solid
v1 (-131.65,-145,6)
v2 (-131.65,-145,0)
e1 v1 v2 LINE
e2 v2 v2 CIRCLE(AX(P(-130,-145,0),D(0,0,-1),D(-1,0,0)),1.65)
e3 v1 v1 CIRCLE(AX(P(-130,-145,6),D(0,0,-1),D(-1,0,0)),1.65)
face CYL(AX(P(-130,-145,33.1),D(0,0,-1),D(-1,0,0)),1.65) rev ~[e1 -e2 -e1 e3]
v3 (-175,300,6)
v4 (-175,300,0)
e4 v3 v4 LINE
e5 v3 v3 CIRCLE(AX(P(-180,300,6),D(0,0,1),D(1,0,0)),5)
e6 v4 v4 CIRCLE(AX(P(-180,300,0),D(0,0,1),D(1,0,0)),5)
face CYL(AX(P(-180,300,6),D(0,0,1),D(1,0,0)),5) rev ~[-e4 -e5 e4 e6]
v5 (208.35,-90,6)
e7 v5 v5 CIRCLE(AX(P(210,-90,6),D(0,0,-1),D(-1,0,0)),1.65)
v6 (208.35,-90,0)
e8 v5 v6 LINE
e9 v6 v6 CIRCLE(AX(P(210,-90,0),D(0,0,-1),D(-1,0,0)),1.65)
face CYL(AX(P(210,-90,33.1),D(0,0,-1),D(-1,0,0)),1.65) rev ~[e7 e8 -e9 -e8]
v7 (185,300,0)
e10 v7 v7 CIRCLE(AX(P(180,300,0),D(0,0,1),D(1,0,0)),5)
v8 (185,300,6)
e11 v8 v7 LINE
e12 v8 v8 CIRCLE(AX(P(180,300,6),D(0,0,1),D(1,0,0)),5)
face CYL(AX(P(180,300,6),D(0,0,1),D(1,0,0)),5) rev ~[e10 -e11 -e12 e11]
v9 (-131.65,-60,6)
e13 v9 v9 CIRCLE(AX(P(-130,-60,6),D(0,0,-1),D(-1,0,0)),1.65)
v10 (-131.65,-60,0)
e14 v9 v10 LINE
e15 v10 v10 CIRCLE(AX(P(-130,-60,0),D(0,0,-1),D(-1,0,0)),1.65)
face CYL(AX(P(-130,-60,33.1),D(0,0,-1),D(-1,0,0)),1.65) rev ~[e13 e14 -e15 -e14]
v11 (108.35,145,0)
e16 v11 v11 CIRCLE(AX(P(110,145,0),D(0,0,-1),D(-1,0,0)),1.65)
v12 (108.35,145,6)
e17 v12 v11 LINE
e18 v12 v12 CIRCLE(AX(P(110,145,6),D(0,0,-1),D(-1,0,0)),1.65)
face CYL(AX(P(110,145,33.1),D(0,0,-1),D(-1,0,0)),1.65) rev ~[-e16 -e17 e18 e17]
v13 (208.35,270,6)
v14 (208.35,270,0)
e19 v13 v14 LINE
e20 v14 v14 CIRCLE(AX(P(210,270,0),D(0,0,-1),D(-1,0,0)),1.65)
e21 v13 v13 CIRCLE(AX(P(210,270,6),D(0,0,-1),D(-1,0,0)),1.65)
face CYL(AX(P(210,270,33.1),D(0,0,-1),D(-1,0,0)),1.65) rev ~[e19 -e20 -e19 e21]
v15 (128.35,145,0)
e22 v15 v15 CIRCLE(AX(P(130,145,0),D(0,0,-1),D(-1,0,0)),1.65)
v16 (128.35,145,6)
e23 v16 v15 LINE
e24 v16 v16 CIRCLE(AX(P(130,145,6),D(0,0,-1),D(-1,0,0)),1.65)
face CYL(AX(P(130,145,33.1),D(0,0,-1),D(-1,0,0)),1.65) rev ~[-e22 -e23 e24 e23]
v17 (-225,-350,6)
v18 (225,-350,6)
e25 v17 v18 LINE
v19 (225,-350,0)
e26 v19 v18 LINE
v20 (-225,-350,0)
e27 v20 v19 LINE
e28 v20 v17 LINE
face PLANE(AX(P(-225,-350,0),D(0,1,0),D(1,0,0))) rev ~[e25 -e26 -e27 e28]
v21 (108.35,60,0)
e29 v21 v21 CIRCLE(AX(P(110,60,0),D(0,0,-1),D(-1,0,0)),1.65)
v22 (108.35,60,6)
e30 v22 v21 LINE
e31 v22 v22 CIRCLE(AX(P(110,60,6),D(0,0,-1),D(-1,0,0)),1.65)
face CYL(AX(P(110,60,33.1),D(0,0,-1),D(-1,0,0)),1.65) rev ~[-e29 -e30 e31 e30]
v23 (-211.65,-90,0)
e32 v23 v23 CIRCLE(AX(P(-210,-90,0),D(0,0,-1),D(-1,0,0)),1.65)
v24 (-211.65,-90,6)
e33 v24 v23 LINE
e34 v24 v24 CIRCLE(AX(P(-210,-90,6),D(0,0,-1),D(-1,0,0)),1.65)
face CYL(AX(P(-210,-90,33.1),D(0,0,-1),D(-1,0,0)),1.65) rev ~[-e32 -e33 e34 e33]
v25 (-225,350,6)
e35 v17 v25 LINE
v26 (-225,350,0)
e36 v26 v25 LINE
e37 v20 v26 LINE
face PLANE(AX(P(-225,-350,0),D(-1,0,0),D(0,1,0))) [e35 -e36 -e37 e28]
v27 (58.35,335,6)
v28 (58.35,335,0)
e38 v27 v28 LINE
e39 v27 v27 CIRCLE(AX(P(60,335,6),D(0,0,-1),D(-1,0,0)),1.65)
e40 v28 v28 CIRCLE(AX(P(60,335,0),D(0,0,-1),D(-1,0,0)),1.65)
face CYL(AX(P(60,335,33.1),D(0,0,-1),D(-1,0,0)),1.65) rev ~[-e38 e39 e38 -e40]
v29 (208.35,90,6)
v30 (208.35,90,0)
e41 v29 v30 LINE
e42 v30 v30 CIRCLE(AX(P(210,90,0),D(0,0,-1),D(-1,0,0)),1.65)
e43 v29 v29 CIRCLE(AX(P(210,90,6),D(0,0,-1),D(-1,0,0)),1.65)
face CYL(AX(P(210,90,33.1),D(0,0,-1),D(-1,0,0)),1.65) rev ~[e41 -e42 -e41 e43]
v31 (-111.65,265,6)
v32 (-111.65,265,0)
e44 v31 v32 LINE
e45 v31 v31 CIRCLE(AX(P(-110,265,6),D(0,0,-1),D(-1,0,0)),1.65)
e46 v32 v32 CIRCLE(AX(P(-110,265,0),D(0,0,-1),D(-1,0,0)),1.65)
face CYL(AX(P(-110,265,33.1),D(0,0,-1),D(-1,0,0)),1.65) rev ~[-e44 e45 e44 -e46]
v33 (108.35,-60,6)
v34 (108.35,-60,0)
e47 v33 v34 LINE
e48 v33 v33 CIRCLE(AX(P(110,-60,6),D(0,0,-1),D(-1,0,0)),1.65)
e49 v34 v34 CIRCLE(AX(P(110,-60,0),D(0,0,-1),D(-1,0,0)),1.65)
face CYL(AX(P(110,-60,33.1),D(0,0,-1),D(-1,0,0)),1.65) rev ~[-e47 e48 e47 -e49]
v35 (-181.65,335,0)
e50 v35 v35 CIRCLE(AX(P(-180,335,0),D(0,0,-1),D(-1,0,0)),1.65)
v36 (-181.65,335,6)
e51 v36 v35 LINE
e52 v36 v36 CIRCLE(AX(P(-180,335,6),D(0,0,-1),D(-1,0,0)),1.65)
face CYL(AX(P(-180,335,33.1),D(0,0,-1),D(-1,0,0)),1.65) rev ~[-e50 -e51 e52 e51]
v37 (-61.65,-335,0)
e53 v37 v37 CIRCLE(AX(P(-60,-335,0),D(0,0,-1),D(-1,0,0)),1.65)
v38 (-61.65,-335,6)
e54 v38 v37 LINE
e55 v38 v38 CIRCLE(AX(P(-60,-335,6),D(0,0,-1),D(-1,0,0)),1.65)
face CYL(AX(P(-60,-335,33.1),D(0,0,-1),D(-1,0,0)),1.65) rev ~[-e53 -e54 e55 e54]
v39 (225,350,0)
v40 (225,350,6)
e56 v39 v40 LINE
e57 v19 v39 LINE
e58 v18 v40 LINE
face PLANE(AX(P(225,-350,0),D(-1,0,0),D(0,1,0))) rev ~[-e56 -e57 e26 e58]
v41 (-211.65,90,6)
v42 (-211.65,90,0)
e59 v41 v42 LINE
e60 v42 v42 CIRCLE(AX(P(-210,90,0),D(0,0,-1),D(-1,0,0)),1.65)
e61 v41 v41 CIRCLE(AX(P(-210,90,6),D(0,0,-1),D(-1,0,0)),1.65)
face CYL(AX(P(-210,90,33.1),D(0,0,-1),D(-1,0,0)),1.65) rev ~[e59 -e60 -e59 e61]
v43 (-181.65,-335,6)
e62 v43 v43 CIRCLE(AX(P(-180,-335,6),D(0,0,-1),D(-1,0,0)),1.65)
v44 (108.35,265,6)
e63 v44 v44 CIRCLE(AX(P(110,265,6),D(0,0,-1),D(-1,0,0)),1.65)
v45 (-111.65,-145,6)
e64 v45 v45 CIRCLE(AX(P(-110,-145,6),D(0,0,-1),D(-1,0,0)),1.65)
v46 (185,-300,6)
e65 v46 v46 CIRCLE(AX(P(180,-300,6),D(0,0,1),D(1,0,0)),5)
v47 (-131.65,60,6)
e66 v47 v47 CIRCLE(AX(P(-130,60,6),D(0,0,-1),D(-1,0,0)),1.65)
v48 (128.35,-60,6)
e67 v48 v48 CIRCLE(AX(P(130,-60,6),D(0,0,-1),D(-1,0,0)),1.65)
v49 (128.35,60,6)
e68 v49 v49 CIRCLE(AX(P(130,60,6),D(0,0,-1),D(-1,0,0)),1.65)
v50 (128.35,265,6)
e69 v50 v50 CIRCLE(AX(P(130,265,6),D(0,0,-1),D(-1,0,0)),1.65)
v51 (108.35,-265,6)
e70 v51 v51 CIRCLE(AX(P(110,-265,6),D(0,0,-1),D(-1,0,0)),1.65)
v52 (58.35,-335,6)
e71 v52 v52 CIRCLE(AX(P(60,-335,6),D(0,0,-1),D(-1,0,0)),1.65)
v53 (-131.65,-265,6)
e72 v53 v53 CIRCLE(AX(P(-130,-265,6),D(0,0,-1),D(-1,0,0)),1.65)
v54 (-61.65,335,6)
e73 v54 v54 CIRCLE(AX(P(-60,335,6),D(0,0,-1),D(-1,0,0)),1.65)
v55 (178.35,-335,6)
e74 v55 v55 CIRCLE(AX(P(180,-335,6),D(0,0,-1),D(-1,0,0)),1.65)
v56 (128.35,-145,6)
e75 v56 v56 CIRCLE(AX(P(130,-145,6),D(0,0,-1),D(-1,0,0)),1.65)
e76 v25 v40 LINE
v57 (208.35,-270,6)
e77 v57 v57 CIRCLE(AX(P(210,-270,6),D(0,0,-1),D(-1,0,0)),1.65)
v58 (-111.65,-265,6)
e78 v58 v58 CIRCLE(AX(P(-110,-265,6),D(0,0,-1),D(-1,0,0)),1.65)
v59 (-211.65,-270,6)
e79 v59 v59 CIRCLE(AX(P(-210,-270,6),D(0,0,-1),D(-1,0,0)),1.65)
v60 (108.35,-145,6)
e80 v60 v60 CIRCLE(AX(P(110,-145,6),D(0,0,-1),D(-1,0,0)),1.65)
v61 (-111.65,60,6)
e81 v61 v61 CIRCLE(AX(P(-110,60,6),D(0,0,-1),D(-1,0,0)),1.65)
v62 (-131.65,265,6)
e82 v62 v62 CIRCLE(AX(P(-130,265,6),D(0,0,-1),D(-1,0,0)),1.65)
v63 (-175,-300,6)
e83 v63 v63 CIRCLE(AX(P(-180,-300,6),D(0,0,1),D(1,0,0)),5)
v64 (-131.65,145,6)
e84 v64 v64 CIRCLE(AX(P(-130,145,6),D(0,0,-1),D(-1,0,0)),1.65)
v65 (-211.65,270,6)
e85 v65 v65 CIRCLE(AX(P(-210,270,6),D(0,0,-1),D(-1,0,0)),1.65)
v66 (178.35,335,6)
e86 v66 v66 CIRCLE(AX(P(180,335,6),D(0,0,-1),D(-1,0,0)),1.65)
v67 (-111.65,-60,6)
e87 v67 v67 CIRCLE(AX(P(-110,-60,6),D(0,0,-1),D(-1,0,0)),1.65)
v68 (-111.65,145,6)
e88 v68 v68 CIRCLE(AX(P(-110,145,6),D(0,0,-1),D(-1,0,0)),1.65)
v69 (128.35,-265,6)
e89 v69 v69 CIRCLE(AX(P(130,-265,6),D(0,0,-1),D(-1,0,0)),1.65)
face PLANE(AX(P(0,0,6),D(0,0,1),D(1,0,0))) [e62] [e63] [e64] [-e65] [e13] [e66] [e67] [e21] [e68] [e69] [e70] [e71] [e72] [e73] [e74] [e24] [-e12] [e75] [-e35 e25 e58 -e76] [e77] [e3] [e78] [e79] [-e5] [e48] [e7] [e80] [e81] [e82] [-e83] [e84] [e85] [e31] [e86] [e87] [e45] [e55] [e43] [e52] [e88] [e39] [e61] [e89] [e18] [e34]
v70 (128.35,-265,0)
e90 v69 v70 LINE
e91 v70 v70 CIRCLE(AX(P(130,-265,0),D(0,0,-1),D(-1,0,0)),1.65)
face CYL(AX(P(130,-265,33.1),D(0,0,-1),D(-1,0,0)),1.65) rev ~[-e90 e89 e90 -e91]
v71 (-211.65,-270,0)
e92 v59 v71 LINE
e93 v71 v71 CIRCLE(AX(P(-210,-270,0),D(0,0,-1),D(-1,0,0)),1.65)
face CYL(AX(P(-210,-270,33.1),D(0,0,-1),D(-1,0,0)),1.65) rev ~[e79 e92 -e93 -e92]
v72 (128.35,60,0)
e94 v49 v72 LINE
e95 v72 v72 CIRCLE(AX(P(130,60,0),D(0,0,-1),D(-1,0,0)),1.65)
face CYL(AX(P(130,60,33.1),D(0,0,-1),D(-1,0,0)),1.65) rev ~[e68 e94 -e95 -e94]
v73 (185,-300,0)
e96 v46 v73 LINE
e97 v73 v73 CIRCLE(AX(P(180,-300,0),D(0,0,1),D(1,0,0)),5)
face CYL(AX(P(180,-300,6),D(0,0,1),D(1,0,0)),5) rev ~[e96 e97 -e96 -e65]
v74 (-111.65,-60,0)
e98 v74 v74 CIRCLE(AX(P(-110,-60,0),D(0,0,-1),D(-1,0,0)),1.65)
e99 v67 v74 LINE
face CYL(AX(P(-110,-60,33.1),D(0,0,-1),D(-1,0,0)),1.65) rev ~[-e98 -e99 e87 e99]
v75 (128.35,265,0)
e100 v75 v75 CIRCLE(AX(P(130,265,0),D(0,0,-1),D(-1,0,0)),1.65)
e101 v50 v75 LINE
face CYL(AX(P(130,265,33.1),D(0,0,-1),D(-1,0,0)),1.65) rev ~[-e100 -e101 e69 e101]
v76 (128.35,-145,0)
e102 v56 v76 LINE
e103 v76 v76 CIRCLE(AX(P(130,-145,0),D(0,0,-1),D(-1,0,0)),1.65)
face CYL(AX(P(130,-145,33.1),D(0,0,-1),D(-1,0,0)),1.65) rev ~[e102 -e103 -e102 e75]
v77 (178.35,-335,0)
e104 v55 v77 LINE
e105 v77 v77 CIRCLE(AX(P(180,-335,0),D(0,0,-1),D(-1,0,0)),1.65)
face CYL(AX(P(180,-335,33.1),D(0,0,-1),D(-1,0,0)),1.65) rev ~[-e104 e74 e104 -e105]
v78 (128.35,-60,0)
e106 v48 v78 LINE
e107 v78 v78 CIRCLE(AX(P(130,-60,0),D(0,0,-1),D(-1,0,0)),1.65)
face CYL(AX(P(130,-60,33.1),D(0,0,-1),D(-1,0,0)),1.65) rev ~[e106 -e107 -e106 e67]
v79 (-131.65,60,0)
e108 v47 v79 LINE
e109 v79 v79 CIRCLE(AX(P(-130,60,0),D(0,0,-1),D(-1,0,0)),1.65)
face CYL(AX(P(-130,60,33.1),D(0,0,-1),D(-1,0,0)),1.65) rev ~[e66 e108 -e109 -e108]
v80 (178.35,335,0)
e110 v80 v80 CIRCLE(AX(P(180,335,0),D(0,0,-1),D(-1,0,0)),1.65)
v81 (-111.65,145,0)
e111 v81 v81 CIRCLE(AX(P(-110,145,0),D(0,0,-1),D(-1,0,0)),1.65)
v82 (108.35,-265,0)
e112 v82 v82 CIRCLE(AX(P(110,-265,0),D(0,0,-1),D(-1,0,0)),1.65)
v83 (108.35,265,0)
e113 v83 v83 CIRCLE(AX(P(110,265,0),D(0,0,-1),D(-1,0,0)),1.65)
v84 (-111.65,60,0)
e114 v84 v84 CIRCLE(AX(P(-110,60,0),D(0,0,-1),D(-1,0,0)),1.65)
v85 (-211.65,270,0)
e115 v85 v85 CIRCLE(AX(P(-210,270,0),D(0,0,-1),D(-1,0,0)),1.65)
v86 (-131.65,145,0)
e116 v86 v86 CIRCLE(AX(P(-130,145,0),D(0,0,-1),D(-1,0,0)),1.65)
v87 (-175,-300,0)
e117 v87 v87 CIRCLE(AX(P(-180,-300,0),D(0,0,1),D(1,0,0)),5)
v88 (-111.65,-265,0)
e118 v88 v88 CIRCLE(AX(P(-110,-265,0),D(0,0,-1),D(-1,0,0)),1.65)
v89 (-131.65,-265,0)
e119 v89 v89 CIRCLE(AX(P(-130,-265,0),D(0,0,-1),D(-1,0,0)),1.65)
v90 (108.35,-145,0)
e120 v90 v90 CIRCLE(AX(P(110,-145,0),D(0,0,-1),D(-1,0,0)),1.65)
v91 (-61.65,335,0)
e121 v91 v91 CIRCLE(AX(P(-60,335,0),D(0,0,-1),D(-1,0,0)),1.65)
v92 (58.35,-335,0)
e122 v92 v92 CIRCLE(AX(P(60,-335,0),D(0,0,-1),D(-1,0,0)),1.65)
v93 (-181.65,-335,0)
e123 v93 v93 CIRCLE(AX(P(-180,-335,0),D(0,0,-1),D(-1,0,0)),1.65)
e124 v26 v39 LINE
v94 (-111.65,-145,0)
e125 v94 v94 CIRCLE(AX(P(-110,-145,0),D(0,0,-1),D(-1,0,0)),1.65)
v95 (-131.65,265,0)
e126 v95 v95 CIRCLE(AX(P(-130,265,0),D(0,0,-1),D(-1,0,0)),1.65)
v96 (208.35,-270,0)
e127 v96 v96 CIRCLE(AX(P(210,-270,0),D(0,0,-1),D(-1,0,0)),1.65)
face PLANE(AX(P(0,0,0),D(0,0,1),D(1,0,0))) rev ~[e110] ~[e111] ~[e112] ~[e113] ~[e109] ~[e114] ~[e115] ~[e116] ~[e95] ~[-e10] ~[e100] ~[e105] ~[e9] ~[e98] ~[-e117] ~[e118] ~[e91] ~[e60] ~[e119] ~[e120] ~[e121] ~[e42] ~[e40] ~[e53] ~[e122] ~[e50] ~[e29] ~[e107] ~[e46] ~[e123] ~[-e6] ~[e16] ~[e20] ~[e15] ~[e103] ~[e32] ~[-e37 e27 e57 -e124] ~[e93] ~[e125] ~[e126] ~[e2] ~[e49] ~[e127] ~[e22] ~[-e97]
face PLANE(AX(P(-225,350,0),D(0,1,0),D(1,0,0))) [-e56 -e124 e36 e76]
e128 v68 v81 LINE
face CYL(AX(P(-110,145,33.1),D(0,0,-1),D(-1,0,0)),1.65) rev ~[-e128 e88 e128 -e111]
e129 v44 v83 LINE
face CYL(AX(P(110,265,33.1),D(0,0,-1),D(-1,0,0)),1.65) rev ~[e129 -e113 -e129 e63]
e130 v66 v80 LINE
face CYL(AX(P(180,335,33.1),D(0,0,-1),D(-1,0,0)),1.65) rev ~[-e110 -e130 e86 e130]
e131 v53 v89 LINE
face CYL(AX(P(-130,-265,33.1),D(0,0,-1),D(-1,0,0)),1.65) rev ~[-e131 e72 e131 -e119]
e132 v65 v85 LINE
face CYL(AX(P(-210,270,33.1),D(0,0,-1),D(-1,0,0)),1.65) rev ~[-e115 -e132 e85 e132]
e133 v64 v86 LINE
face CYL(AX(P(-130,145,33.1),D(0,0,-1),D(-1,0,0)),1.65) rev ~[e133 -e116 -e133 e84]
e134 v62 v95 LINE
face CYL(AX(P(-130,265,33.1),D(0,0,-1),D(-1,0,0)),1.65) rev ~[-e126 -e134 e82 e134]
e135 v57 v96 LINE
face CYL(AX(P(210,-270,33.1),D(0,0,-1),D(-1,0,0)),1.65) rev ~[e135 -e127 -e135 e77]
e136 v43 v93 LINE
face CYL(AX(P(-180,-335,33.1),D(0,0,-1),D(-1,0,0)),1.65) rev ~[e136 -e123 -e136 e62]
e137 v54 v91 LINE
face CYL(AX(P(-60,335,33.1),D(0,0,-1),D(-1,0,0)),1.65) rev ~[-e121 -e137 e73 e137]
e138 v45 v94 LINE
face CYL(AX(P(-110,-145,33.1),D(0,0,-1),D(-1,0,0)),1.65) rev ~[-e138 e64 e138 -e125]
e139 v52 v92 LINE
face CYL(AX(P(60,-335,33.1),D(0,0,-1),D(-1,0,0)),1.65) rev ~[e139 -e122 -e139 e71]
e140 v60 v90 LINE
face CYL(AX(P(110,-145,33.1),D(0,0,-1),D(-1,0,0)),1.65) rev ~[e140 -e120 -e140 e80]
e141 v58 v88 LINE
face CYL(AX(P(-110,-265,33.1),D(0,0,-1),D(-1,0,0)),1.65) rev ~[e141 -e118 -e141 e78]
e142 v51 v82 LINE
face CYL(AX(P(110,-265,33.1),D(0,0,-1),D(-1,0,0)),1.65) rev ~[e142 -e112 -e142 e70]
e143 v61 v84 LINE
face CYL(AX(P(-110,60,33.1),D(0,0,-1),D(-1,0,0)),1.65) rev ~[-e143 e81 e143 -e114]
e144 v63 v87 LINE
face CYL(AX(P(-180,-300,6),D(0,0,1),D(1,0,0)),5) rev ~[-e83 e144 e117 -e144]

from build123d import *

# Parameters (mm, degrees)
SKETCH_1_W             = 450
SKETCH_1_H             = 700
EXTRUDE_1_DEPTH        = 6
HOLE_WIZARD_M4_1_D     = 3.3
HOLE_WIZARD_M4_1_DEPTH = 27.1
HOLE_WIZARD_M4_1_TIP   = 0.991420021
HOLE_WIZARD_M4_2_D     = 3.3
HOLE_WIZARD_M4_2_DEPTH = 27.1
HOLE_WIZARD_M4_2_TIP   = 0.991420021
SKETCH_7_R             = 5
CUT_EXTRUDE_1_DEPTH    = 10


with BuildPart() as part:
    # 草图1 → 凸台-拉伸1 (new body)
    with BuildSketch(Plane.XY):
        Rectangle(SKETCH_1_W, SKETCH_1_H)
    extrude(amount=EXTRUDE_1_DEPTH)

    # M4 螺纹孔1
    with Locations(Plane.XY.offset(6)):
        with Locations((130, -265), (110, -265), (110, -145), (130, -145), (110, -60), (130, -60), (130, 60), (110, 60), (-130, -265), (-110, -265), (-130, -145), (-110, -145), (-130, -60), (-110, -60), (-130, 60), (-110, 60), (-130, 145), (-110, 145), (-130, 265), (-110, 265), (110, 145), (130, 145), (110, 265), (130, 265)):
            Hole(HOLE_WIZARD_M4_1_D / 2, depth=HOLE_WIZARD_M4_1_DEPTH)
            with Locations((0, 0, -(HOLE_WIZARD_M4_1_DEPTH + HOLE_WIZARD_M4_1_TIP / 2))):  # 118° drill point
                Cone(0, HOLE_WIZARD_M4_1_D / 2, HOLE_WIZARD_M4_1_TIP, mode=Mode.SUBTRACT)

    # M4 螺纹孔2
    with Locations(Plane.XY.offset(6)):
        with Locations((-180, 335), (-60, 335), (60, 335), (180, 335), (-180, -335), (-60, -335), (60, -335), (180, -335), (210, -270), (210, -90), (210, 90), (210, 270), (-210, 270), (-210, 90), (-210, -90), (-210, -270)):
            Hole(HOLE_WIZARD_M4_2_D / 2, depth=HOLE_WIZARD_M4_2_DEPTH)
            with Locations((0, 0, -(HOLE_WIZARD_M4_2_DEPTH + HOLE_WIZARD_M4_2_TIP / 2))):  # 118° drill point
                Cone(0, HOLE_WIZARD_M4_2_D / 2, HOLE_WIZARD_M4_2_TIP, mode=Mode.SUBTRACT)

    # 草图7 → 切除-拉伸1 (cut)
    with BuildSketch(Plane.XY.offset(6)):
        with Locations((180, -300)):
            Circle(SKETCH_7_R)
        with Locations((-180, -300)):
            Circle(SKETCH_7_R)
        with Locations((-180, 300)):
            Circle(SKETCH_7_R)
        with Locations((180, 300)):
            Circle(SKETCH_7_R)
    extrude(amount=-CUT_EXTRUDE_1_DEPTH, mode=Mode.SUBTRACT)


solid = part.part
